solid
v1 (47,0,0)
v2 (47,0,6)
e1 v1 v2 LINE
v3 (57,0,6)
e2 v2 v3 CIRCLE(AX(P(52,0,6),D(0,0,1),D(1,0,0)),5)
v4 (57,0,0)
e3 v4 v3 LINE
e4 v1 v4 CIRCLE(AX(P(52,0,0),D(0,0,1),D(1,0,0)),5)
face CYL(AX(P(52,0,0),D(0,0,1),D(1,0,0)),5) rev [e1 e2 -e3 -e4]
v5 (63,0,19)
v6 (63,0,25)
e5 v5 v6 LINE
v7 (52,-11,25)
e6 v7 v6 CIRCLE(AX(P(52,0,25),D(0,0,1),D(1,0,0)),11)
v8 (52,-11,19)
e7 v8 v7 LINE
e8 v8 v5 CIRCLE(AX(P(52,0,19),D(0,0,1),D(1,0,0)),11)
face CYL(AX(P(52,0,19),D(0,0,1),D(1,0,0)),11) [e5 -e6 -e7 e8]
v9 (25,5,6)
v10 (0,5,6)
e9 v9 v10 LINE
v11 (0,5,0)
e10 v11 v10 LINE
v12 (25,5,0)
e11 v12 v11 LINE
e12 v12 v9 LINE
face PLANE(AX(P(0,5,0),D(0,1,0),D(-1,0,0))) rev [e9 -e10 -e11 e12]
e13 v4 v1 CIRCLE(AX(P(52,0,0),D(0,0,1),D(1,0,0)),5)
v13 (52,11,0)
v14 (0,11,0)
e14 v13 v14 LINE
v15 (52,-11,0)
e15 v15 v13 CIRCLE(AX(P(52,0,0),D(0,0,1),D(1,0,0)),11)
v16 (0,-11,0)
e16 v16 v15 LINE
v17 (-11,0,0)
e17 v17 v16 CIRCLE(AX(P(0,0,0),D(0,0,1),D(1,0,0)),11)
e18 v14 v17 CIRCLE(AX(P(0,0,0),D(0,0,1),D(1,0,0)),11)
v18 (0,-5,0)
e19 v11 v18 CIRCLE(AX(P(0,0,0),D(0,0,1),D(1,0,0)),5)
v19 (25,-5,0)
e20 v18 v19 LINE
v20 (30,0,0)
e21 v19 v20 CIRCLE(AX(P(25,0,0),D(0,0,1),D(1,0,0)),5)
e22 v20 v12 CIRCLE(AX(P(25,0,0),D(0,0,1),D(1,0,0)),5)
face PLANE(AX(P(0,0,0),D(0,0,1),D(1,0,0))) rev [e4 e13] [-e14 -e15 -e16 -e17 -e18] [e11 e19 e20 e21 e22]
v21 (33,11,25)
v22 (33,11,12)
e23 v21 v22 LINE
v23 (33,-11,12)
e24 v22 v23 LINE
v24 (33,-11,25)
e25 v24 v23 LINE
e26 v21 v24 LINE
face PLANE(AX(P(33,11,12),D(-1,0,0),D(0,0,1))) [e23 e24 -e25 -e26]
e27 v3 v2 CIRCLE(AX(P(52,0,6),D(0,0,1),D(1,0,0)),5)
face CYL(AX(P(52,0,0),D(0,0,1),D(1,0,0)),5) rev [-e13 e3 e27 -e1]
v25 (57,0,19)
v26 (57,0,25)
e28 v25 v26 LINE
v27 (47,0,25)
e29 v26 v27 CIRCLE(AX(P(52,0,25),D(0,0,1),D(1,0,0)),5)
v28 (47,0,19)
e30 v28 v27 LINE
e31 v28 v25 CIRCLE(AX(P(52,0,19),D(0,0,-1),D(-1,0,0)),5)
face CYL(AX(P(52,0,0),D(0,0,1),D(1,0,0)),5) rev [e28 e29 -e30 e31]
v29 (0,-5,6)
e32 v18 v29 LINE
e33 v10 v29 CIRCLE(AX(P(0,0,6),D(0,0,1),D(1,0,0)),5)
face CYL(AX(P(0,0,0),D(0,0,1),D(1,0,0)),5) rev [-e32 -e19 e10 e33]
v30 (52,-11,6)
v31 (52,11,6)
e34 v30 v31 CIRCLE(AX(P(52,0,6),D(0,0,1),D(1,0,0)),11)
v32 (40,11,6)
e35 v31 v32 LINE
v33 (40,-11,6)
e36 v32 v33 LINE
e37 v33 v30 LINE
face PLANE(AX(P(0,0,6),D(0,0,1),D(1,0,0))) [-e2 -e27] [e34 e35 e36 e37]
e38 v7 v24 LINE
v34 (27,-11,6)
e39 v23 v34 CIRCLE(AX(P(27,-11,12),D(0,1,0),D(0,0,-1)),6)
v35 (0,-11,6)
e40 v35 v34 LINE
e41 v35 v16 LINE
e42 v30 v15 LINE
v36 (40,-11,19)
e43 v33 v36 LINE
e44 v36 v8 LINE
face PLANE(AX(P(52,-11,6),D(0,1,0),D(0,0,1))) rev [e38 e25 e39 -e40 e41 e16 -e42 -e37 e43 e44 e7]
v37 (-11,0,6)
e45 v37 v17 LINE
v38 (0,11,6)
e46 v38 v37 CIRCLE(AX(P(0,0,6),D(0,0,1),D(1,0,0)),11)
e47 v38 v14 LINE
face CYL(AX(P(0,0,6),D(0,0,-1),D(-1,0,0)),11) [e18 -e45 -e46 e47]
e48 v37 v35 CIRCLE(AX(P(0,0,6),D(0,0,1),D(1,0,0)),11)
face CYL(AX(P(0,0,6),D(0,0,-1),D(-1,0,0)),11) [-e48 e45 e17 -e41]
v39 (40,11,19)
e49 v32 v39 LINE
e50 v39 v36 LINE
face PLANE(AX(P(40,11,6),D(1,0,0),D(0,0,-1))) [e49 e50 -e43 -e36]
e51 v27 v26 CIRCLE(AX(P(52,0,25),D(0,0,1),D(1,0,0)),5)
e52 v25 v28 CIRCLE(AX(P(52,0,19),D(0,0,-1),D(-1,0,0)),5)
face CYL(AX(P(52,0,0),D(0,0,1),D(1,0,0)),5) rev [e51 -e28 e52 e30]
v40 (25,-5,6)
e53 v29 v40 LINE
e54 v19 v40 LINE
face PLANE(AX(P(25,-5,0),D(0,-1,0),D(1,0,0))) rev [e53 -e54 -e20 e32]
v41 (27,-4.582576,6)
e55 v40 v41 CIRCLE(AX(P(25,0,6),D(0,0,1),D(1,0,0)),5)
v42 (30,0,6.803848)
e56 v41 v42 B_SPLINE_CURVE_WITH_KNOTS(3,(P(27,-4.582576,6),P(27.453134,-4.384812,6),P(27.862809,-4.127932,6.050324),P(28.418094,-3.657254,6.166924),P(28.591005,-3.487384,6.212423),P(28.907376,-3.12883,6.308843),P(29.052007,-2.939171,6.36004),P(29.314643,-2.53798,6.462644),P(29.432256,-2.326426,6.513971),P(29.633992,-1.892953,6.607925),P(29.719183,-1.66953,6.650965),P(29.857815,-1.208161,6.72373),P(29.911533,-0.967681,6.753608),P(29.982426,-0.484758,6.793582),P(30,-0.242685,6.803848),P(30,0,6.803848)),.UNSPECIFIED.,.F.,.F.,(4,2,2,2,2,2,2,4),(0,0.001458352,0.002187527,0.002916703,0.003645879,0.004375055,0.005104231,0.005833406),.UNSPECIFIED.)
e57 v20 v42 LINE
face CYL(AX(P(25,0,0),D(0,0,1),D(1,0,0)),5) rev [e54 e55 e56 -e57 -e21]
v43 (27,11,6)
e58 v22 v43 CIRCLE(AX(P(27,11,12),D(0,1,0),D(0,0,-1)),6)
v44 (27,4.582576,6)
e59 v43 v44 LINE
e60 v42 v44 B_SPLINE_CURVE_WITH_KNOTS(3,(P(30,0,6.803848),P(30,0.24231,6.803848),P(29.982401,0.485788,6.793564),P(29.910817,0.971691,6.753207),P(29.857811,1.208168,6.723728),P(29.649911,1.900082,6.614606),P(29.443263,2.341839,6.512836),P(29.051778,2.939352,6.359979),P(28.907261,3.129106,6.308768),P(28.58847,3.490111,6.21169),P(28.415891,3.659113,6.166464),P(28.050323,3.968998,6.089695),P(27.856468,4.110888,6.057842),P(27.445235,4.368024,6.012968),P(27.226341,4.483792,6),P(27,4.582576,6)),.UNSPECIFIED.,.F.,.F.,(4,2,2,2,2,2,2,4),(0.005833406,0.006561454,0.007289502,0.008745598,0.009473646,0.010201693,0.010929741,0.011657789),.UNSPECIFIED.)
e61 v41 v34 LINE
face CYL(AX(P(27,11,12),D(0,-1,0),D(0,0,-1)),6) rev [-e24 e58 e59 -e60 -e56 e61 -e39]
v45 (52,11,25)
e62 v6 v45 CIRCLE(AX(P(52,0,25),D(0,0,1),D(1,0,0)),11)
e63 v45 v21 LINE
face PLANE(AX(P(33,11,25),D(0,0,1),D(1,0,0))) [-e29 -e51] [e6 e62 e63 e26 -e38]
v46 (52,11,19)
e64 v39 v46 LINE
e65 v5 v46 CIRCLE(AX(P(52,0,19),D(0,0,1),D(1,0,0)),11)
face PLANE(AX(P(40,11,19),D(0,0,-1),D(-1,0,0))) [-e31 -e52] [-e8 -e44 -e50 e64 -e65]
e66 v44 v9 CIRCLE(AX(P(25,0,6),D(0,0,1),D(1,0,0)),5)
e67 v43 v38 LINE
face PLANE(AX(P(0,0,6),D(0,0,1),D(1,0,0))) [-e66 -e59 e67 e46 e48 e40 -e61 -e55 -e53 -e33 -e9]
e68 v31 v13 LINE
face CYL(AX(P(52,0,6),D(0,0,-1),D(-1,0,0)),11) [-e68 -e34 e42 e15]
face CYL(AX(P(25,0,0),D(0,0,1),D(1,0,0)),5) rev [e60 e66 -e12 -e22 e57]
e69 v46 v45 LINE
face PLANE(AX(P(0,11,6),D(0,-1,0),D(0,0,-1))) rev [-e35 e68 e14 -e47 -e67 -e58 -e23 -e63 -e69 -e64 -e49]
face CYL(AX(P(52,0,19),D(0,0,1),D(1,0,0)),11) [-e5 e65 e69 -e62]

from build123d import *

# Parameters (mm, degrees)
BASE_BLOCK_22X22_DEPTH    = 6
SQUARE_CUTOUT_10X10_DEPTH = 6
LINK_BODY_DEPTH           = 22
LINK_START                = -22
LINK_SLOT_DEPTH           = 22
END_START                 = -6
END_TAB_DEPTH             = 6
CROSS_HOLE_SKETCH_R       = 5
CROSS_HOLE_10_DEPTH       = 25


with BuildPart() as part:
    # Base Block Sketch → Base Block 22x22 (new body)
    with BuildSketch(Plane.XY):
        with BuildLine():
            Line((0, 11), (52, 11))
            ThreePointArc((52, 11), (63, 0), (52, -11))
            Line((52, -11), (0, -11))
            ThreePointArc((0, -11), (-11, 0), (0, 11))
        make_face()
    extrude(amount=BASE_BLOCK_22X22_DEPTH)

    # Square Cutout Sketch → Square Cutout 10x10 (cut)
    with BuildSketch(Plane.XY.offset(6)):
        with BuildLine():
            Line((0, 5), (25, 5))
            ThreePointArc((25, 5), (30, 0), (25, -5))
            Line((25, -5), (0, -5))
            ThreePointArc((0, -5), (-5, 0), (0, 5))
        make_face()
    extrude(amount=-SQUARE_CUTOUT_10X10_DEPTH, mode=Mode.SUBTRACT)

    # Link Profile Sketch → Link Body (add)
    with BuildSketch(Plane.XZ.offset(11)):
        with BuildLine():
            Line((27, 6), (33, 6))
            Line((33, 6), (40, 6))
            Line((40, 6), (40, 19))
            Line((40, 19), (52, 19))
            Line((52, 19), (52, 25))
            Line((52, 25), (33, 25))
            Line((33, 25), (33, 19))
            Line((33, 19), (33, 12))
            ThreePointArc((33, 12), (31.242640687, 7.757359313), (27, 6))
        make_face()
    extrude(amount=-LINK_BODY_DEPTH)

    # Link Slot Sketch → Link Slot (cut)
    with BuildSketch(Plane(origin=(0, 0, 6), x_dir=(-1, 0, 0), z_dir=(0, 0, -1)).offset(LINK_START)):
        with BuildLine():
            Line((-27, 4.582575695), (-27, -4.582575695))
            ThreePointArc((-27, -4.582575695), (-30, 0), (-27, 4.582575695))
        make_face()
    extrude(amount=LINK_SLOT_DEPTH, mode=Mode.SUBTRACT)

    # End Tab Sketch → End Tab (add)
    with BuildSketch(Plane.XY.offset(25).offset(END_START)):
        with BuildLine():
            Line((52, 11), (52, -11))
            ThreePointArc((52, -11), (63, 0), (52, 11))
        make_face()
    extrude(amount=END_TAB_DEPTH)

    # Cross Hole Sketch → Cross Hole Ø10 (cut)
    with BuildSketch(Plane.XY.offset(25)):
        with Locations((52, 0)):
            Circle(CROSS_HOLE_SKETCH_R)
    extrude(amount=-CROSS_HOLE_10_DEPTH, mode=Mode.SUBTRACT)


solid = part.part
